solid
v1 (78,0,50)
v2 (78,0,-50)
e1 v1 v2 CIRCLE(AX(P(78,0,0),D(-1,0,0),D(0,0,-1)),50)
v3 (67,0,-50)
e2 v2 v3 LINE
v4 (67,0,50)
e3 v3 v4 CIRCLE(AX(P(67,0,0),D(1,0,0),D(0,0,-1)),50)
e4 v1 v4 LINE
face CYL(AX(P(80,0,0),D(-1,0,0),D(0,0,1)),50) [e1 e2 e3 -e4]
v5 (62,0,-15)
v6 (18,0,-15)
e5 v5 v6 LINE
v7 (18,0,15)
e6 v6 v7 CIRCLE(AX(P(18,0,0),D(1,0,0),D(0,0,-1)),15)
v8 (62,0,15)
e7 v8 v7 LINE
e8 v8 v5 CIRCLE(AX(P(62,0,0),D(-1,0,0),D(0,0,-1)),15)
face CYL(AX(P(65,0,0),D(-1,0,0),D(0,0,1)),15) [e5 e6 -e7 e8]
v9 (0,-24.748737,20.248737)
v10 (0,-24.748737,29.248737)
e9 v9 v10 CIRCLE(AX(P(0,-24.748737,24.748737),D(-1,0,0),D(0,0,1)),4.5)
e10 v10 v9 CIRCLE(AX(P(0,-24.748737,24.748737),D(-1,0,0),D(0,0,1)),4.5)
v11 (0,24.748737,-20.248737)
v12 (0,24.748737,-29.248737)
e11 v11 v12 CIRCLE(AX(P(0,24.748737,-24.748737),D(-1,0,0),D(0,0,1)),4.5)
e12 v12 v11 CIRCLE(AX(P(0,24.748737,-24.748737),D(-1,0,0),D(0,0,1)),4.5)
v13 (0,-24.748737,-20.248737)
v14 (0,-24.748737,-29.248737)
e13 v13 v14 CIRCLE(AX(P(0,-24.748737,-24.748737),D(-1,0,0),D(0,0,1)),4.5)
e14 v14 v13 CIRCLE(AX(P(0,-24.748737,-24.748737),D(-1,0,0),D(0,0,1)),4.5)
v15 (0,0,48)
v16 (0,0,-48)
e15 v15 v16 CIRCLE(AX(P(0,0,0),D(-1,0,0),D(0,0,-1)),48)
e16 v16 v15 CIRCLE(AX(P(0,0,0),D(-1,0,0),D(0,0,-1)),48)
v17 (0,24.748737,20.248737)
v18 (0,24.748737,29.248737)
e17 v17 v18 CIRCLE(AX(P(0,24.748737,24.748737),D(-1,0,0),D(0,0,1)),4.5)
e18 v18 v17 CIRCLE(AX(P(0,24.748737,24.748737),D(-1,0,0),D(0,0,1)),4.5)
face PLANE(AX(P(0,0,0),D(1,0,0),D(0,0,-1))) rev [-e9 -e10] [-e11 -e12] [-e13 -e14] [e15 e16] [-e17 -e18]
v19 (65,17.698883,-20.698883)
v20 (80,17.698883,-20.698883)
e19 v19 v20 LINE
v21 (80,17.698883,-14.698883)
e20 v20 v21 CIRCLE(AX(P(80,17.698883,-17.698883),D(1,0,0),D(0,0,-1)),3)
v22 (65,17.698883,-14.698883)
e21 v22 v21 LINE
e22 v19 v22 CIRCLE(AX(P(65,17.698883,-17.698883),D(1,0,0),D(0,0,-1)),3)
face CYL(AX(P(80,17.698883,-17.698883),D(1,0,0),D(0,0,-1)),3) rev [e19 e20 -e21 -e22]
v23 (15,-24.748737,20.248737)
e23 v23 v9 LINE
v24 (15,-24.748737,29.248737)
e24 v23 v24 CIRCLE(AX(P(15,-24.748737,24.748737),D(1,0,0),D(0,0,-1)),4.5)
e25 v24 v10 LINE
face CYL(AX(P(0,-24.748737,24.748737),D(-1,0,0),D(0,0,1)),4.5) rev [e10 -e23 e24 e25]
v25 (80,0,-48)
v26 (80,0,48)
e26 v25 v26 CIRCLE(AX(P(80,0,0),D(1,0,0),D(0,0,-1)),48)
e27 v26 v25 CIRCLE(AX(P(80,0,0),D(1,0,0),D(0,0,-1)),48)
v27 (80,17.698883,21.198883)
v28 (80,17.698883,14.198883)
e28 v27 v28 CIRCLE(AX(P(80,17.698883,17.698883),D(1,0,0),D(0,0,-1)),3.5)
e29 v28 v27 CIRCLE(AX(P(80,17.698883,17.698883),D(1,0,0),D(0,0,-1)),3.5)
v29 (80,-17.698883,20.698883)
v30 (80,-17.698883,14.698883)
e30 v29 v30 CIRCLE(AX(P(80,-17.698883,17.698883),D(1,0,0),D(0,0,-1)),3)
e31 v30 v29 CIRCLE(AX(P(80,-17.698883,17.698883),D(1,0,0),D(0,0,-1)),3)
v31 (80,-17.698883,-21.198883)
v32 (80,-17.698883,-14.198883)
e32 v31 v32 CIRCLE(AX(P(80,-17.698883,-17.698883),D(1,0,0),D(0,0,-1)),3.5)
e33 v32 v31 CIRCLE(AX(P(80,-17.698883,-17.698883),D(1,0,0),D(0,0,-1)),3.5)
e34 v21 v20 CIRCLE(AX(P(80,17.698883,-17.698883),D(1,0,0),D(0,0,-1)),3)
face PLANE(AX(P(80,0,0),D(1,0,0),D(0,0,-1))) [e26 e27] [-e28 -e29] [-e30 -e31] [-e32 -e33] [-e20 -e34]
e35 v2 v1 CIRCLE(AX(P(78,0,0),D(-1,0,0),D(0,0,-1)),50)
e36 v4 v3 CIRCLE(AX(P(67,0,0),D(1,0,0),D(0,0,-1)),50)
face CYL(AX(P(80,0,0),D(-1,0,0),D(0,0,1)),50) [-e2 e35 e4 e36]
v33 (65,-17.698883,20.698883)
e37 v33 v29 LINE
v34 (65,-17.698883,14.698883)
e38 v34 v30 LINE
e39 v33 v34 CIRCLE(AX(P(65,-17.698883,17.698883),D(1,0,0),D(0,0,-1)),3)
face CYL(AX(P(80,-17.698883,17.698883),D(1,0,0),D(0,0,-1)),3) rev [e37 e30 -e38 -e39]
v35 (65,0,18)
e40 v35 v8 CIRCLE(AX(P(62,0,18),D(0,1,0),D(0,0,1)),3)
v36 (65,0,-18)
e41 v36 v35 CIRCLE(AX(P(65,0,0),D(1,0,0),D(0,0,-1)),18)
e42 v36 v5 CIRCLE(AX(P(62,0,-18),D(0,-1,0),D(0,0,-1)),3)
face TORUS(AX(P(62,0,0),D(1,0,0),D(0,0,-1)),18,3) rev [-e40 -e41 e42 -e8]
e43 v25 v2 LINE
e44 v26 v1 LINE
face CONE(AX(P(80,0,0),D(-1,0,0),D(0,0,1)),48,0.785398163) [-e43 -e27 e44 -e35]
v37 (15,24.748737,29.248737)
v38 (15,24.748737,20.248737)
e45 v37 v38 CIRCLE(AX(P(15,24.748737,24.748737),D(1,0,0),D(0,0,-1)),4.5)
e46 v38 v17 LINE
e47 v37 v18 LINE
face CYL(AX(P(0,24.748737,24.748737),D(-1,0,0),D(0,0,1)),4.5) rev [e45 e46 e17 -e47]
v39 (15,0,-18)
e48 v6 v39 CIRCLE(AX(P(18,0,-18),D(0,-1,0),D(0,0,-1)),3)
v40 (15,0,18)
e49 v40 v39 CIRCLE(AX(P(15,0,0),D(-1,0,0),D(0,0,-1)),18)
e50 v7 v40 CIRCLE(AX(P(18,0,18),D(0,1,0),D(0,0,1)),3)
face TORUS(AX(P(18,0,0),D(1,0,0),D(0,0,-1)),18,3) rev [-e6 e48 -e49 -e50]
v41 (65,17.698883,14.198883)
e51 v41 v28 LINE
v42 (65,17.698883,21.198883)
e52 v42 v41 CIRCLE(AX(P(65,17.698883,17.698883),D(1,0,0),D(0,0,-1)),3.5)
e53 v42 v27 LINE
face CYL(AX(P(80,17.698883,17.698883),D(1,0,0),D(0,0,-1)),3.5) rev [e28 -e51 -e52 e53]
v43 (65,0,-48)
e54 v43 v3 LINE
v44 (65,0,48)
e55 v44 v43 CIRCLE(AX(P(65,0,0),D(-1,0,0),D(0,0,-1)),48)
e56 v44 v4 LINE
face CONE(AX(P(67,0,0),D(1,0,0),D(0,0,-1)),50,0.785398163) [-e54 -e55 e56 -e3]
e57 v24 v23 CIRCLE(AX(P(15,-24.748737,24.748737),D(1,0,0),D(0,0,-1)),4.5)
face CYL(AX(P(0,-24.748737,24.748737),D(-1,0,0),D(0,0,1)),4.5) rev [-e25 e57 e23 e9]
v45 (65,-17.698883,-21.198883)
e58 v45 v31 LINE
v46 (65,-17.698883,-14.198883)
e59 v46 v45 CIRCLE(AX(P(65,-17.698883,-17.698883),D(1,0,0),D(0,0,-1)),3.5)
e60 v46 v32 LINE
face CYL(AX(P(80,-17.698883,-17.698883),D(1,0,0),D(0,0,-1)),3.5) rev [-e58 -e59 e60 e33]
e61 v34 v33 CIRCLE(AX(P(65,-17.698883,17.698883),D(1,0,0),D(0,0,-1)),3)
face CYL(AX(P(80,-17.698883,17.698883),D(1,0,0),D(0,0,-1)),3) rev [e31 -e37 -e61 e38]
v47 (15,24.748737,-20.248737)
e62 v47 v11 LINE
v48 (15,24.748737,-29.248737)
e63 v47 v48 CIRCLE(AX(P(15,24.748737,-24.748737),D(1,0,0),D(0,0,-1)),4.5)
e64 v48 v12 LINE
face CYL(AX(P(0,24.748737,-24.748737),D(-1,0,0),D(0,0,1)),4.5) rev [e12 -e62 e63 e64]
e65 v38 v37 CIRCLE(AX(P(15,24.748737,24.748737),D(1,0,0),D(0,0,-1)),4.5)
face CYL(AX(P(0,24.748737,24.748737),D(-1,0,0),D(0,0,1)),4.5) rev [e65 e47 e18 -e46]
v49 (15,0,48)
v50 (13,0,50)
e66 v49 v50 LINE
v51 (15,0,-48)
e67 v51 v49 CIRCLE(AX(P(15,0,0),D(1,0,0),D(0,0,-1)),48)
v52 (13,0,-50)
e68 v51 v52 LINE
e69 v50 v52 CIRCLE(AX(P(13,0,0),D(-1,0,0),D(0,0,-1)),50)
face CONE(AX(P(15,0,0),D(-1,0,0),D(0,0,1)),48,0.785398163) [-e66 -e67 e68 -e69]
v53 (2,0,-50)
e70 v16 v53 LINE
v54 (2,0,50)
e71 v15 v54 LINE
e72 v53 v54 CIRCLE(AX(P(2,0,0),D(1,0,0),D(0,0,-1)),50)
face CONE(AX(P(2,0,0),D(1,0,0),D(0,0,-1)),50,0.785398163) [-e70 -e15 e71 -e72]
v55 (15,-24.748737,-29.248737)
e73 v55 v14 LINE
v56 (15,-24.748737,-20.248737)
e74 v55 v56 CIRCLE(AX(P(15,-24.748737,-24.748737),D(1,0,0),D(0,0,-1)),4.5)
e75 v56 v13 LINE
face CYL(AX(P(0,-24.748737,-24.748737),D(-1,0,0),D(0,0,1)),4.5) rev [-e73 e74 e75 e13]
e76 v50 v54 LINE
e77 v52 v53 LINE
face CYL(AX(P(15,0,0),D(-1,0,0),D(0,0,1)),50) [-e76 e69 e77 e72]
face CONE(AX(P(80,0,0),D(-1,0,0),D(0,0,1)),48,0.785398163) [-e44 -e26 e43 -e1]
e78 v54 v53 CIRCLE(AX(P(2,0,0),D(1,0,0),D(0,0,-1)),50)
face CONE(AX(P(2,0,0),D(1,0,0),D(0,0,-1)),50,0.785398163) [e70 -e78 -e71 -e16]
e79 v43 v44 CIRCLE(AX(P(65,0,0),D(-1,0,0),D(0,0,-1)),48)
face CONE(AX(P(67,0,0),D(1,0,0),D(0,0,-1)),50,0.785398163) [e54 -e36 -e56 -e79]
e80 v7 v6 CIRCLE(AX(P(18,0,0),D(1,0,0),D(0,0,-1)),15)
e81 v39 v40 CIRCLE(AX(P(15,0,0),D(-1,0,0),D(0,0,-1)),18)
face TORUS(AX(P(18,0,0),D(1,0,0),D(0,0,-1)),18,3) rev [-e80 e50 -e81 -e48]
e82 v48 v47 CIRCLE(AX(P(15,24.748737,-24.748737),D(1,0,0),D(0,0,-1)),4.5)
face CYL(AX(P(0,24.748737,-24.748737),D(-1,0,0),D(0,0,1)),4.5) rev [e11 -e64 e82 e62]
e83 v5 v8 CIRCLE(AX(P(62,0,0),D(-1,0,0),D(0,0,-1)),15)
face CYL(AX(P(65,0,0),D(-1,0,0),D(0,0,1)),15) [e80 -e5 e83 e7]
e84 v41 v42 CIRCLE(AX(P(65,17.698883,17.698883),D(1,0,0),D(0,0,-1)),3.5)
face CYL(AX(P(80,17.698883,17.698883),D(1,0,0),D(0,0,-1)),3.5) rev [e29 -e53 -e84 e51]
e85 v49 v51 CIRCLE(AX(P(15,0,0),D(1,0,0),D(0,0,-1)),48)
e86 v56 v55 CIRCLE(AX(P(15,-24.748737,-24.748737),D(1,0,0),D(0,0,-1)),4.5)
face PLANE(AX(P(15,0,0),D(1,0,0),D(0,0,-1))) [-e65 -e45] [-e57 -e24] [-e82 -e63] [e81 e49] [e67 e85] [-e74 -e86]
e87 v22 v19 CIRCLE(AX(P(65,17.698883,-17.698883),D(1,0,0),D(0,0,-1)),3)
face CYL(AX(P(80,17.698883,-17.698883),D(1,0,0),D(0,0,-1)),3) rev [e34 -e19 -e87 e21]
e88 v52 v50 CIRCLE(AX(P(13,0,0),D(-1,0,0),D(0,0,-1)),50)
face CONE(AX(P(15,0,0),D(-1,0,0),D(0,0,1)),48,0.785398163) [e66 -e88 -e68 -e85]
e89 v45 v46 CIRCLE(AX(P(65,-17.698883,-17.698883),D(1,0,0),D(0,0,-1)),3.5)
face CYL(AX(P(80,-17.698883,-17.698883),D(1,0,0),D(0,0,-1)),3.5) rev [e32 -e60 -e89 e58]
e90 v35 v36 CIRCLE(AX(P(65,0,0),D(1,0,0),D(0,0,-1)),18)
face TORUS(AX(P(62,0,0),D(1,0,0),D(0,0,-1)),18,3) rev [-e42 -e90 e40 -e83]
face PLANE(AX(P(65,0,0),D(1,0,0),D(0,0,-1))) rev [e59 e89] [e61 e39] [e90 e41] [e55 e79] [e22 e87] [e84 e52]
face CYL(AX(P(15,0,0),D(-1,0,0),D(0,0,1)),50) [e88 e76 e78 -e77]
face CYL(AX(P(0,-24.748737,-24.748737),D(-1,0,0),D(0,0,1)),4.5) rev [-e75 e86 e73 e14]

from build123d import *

# Parameters (mm, degrees)
SKETCH_1_R                = 50
EXTRUDE_1_DEPTH           = 15
SKETCH_2_R                = 15
EXTRUDE_2_DEPTH           = 50
SKETCH_3_R                = 50
EXTRUDE_3_DEPTH           = 15
HOLE_WIZARD_7_0_7_1_D     = 7
HOLE_WIZARD_7_0_7_1_DEPTH = 19.75
HOLE_WIZARD_7_0_7_1_TIP   = 2.103012167
MM_1_D                    = 6
MM_1_DEPTH                = 19.75
MM_1_TIP                  = 1.802581857
PATTERN_CIRCULAR_1_COUNT  = 4
FILLET_1_R                = 3
CHAMFER_1_SIZE            = 2


with BuildPart() as part:
    # 草图1 → 凸台-拉伸1 (new body)
    with BuildSketch(Plane(origin=(0, 0, 0), x_dir=(0, 0, -1), z_dir=(1, 0, 0))):
        Circle(SKETCH_1_R)
    extrude(amount=EXTRUDE_1_DEPTH)

    # 草图2 → 凸台-拉伸2 (add)
    with BuildSketch(Plane(origin=(15, 0, 0), x_dir=(0, 0, -1), z_dir=(1, 0, 0))):
        Circle(SKETCH_2_R)
    extrude(amount=EXTRUDE_2_DEPTH)

    # 草图3 → 凸台-拉伸3 (add)
    with BuildSketch(Plane(origin=(65, 0, 0), x_dir=(0, 0, -1), z_dir=(1, 0, 0))):
        Circle(SKETCH_3_R)
    extrude(amount=EXTRUDE_3_DEPTH)

    # Ø7.0 (7) 直径孔1
    with Locations(Plane(origin=(80, 0, 0), x_dir=(0, 0, -1), z_dir=(1, 0, 0))):
        with Locations((-17.698882733, 17.698882733), (17.698882733, -17.698882733)):
            Hole(HOLE_WIZARD_7_0_7_1_D / 2, depth=HOLE_WIZARD_7_0_7_1_DEPTH)
            with Locations((0, 0, -(HOLE_WIZARD_7_0_7_1_DEPTH + HOLE_WIZARD_7_0_7_1_TIP / 2))):  # 118° drill point
                Cone(0, HOLE_WIZARD_7_0_7_1_D / 2, HOLE_WIZARD_7_0_7_1_TIP, mode=Mode.SUBTRACT)

    # 大小mm 暗销孔1
    with Locations(Plane(origin=(80, 0, 0), x_dir=(0, 0, -1), z_dir=(1, 0, 0))):
        with Locations((-17.698882733, -17.698882733), (17.698882733, 17.698882733)):
            Hole(MM_1_D / 2, depth=MM_1_DEPTH)
            with Locations((0, 0, -(MM_1_DEPTH + MM_1_TIP / 2))):  # 118° drill point
                Cone(0, MM_1_D / 2, MM_1_TIP, mode=Mode.SUBTRACT)

    # 草图9 → Ø9.0 (9) 直径孔1 (revolve, cut)
    with BuildSketch(Plane(origin=(0, 24.748737342, -24.748737342), x_dir=(0, 0, 1), z_dir=(0, 1, 0))):
        Polygon((0, 0), (0, 22.453872786), (4.5, 19.75), (4.5, 0), align=None)
    hole_wizard_9_0_9_1 = revolve(axis=Axis((-6.35, 24.748737342, -24.748737342), (1, 0, 0)), mode=Mode.SUBTRACT)

    # 阵列(圆周)1: Ø9.0 (9) 直径孔1 ×4 about axis
    pattern_circular_1_axis = Axis((0, 0, 0), (1, 0, 0))
    for i in range(1, PATTERN_CIRCULAR_1_COUNT):
        add(hole_wizard_9_0_9_1.rotate(pattern_circular_1_axis, i * 360 / PATTERN_CIRCULAR_1_COUNT), mode=Mode.SUBTRACT)

    # 圆角1
    fillet_1_edges = [part.edges().sort_by_distance(p)[0] for p in [
        (15, 0, 15),
        (65, 0, 15),
    ]]
    fillet(fillet_1_edges, radius=FILLET_1_R)

    # 倒角1
    chamfer_1_edges = [part.edges().sort_by_distance(p)[0] for p in [
        (0, 0, 50),
        (15, 0, 50),
        (65, 0, 50),
        (80, 0, 50),
    ]]
    chamfer(chamfer_1_edges, length=CHAMFER_1_SIZE)


solid = part.part
